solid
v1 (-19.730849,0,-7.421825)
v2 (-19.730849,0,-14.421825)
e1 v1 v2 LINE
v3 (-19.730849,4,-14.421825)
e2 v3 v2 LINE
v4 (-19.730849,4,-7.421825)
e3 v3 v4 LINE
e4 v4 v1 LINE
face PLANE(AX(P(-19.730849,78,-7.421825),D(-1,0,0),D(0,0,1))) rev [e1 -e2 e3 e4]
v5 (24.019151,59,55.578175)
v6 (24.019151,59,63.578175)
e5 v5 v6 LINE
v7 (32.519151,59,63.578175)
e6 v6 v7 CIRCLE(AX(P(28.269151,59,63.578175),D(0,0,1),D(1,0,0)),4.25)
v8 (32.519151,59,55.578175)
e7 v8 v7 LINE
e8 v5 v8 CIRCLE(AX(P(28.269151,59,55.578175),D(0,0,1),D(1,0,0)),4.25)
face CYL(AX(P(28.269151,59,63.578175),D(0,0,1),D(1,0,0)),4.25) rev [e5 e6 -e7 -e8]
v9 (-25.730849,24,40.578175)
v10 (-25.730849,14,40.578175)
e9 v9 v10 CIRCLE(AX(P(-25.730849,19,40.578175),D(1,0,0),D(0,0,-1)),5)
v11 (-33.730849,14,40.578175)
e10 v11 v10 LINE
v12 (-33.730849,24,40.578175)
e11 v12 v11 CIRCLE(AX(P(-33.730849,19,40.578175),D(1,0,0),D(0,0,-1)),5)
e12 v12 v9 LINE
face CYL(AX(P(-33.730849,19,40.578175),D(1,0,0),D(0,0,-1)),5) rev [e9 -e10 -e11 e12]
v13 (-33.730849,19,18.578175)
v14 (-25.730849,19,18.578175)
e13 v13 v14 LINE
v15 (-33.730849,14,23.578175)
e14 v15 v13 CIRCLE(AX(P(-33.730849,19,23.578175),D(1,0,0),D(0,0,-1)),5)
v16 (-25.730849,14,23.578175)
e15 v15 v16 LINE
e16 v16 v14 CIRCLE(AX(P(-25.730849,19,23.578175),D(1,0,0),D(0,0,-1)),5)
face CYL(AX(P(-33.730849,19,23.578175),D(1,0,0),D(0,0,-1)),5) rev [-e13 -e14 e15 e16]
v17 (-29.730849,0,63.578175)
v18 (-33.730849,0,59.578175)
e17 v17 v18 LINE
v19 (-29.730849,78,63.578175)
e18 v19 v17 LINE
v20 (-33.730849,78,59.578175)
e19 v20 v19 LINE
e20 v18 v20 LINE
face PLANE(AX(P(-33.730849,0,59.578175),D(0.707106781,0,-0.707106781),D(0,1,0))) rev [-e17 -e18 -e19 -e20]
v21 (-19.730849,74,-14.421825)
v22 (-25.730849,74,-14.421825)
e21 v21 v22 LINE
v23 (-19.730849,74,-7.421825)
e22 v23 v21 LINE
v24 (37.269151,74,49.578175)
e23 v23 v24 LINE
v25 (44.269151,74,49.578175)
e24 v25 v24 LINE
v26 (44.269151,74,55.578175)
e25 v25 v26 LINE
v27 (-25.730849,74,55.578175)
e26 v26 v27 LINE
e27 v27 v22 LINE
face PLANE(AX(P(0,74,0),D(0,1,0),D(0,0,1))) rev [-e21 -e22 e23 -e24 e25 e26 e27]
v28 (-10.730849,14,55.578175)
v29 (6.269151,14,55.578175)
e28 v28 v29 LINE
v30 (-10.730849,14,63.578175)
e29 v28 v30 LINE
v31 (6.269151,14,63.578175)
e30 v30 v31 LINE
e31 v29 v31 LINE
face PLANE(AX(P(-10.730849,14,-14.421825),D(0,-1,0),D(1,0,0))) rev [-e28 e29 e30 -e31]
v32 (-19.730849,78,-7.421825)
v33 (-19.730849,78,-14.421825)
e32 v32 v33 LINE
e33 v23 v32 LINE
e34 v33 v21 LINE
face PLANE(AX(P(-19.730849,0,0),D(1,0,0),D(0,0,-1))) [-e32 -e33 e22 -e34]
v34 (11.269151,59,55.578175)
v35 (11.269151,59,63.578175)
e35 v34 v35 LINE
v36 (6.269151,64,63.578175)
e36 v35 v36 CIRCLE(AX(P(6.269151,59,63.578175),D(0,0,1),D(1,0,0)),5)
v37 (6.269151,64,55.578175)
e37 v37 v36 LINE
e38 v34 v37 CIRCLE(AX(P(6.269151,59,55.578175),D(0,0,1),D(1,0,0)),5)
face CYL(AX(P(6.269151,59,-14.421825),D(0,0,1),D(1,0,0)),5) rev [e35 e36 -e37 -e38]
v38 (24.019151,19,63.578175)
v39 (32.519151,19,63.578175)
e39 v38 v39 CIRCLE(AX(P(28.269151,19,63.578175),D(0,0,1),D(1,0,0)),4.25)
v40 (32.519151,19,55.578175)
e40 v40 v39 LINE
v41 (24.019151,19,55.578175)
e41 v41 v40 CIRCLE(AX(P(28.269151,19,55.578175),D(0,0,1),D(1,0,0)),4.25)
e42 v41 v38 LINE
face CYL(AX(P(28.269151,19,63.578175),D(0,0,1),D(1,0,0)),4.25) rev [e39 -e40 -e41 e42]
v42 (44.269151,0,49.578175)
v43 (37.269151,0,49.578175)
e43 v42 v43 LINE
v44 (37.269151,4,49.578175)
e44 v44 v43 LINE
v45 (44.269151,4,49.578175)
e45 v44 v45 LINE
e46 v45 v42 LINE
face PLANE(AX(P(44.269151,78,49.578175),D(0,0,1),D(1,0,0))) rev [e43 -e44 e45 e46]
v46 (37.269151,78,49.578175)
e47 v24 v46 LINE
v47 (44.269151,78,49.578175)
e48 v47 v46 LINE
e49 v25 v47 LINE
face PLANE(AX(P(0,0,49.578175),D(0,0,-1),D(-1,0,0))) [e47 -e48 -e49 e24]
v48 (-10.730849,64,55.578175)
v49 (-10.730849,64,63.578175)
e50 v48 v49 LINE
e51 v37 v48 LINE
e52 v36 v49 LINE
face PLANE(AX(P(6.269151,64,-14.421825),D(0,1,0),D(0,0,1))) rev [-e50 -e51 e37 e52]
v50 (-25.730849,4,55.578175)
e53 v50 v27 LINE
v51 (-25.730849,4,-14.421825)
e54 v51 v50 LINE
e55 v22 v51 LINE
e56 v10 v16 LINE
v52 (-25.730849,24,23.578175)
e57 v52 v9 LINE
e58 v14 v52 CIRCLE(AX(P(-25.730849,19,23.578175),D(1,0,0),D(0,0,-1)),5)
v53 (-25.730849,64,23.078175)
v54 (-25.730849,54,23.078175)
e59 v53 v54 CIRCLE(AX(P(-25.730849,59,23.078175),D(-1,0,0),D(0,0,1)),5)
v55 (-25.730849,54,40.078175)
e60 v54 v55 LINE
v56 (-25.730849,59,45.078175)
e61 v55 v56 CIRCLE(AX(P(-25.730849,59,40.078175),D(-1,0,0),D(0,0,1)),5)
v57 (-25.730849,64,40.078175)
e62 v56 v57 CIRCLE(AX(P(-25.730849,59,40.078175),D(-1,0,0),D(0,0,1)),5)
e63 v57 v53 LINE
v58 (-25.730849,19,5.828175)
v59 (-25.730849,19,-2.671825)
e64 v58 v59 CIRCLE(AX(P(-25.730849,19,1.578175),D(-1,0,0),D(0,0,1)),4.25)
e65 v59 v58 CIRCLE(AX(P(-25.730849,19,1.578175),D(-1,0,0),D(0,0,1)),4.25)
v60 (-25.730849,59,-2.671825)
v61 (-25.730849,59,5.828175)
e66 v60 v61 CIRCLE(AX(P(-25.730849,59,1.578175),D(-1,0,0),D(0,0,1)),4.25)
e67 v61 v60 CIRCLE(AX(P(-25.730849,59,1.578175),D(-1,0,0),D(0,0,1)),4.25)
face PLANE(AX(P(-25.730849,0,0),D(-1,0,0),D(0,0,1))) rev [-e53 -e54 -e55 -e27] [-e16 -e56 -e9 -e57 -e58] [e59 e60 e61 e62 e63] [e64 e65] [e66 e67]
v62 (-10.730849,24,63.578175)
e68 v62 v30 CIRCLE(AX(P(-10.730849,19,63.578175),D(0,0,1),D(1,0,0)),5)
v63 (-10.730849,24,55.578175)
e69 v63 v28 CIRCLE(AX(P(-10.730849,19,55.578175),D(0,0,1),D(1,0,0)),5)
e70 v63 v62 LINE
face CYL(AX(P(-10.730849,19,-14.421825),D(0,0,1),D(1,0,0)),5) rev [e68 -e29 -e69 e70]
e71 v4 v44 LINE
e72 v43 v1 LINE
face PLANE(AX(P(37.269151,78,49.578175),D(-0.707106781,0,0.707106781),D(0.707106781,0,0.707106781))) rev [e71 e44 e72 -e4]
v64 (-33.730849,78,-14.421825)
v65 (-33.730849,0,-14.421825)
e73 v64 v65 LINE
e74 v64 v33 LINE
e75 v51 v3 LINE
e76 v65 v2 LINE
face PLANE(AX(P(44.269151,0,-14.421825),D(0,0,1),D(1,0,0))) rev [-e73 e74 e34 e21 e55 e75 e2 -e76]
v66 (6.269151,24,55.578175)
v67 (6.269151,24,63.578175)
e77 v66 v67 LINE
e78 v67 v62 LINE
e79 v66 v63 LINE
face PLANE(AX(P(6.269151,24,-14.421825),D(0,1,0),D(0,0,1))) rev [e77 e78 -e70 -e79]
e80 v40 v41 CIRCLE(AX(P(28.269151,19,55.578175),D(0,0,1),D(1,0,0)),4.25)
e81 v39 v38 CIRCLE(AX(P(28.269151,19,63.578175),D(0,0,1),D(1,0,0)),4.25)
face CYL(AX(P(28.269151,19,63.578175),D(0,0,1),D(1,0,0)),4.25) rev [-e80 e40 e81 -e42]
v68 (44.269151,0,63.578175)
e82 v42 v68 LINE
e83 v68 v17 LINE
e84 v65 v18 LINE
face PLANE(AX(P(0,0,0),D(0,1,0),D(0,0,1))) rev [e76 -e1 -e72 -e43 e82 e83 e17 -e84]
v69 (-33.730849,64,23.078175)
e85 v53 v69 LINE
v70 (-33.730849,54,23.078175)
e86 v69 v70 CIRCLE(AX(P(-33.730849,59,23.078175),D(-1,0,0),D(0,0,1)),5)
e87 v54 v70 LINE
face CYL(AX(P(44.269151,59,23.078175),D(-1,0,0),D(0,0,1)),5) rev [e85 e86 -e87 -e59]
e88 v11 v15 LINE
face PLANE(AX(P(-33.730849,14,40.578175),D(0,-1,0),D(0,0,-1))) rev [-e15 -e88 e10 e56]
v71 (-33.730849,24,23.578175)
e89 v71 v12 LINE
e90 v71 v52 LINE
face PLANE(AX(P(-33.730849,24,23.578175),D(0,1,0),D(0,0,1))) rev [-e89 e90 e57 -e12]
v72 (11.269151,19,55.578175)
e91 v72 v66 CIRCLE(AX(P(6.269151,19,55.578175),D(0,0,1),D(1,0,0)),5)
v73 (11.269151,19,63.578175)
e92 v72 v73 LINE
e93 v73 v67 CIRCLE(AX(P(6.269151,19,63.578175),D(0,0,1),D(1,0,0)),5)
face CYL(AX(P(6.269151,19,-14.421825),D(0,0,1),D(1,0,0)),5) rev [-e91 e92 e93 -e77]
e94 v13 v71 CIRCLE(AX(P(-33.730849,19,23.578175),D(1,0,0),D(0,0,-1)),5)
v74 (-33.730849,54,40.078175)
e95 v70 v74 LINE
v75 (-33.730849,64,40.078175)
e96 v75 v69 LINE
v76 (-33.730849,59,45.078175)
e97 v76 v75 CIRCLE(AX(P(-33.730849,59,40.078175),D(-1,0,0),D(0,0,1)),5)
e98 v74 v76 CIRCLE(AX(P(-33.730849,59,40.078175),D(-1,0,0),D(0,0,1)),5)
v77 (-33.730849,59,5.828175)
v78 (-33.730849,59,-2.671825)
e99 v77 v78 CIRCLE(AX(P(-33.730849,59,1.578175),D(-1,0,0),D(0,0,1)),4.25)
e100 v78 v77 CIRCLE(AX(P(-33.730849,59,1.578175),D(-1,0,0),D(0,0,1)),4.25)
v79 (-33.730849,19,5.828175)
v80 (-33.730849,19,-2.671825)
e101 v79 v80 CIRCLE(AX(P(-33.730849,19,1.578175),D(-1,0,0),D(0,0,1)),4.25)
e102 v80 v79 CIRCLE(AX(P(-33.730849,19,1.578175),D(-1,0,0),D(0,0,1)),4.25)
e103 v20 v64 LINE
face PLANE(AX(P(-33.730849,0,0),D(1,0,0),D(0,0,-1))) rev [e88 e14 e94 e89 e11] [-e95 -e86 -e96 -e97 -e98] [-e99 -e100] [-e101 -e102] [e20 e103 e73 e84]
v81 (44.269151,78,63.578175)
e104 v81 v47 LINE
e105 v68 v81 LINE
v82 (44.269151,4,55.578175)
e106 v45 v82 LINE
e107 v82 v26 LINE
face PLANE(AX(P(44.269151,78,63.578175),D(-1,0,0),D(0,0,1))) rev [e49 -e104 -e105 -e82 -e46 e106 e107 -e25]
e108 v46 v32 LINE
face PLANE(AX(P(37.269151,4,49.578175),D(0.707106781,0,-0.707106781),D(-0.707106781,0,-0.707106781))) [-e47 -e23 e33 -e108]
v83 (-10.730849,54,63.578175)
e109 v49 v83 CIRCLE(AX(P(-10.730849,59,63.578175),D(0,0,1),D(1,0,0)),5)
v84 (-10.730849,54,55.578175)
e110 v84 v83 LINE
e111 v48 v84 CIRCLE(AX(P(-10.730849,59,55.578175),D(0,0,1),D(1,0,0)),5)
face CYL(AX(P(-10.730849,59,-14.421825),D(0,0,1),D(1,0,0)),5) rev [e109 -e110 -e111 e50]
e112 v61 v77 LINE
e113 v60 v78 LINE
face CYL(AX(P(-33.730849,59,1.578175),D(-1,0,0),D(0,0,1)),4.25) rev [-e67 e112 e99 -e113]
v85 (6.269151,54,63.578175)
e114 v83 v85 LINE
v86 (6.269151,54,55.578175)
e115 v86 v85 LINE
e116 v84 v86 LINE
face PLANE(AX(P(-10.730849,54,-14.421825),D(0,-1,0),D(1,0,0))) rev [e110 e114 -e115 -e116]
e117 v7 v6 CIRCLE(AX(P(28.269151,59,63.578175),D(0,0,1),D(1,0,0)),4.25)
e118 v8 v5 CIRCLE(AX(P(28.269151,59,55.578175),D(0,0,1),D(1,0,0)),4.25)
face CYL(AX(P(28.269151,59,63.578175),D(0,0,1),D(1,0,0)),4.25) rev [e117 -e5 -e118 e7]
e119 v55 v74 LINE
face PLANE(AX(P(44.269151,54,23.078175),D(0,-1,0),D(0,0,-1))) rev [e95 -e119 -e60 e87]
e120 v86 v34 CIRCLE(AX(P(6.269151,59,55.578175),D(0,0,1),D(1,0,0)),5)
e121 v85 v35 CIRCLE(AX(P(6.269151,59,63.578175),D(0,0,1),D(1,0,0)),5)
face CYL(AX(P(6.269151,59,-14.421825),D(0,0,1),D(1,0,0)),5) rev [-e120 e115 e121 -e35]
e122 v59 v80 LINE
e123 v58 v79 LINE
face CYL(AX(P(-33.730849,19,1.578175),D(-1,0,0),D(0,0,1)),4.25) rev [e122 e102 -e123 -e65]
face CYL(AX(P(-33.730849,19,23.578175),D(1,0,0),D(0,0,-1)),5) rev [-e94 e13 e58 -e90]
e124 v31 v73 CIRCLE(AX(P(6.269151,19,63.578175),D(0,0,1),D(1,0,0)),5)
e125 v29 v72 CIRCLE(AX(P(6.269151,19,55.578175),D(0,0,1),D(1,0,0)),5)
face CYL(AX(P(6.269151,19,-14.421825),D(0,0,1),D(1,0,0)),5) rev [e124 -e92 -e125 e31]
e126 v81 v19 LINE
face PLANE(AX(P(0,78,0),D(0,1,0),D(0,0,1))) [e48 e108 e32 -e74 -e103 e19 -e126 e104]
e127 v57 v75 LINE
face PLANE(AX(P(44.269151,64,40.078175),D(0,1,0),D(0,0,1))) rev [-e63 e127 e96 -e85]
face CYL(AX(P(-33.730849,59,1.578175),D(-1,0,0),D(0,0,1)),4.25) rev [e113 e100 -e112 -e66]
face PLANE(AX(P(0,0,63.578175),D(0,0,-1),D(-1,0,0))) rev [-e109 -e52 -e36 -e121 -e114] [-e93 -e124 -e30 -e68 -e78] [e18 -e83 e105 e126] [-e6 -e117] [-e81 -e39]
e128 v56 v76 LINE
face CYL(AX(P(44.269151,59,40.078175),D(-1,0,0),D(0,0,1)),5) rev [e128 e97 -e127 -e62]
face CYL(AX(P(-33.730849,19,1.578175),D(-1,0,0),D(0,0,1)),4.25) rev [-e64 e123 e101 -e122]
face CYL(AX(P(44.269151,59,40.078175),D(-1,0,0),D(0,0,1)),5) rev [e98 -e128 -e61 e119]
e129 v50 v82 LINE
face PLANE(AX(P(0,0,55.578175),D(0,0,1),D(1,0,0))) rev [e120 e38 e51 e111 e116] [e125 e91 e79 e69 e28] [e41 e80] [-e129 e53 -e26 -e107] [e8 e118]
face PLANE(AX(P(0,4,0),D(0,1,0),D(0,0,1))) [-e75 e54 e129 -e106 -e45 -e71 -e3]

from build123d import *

# Parameters (mm, degrees)
BOSS_EXTRUDE1_DEPTH            = 74
SKETCH2_W                      = 64
SKETCH2_H                      = 74
BOSS_EXTRUDE2_DEPTH            = 14
SKETCH3_W                      = 64
SKETCH3_H                      = 78
BOSS_EXTRUDE3_DEPTH            = 4
CUT_EXTRUDE1_DEPTH             = 70
SKETCH5_W                      = 78
SKETCH5_H                      = 78
BOSS_EXTRUDE4_DEPTH            = 14
CUT_EXTRUDE2_REACH             = 115.771
SKETCH7_W                      = 64
SKETCH7_H                      = 70
CUT_EXTRUDE3_REACH             = 124.581
SKETCH9_W                      = 70
SKETCH9_H                      = 70
CUT_EXTRUDE4_DEPTH             = 110.936081615
CUT_EXTRUDE5_DEPTH             = 123.581337469
CUT_EXTRUDE6_DEPTH             = 119.860244595
CUT_EXTRUDE7_DEPTH             = 119.860244595
CUT_EXTRUDE8_DEPTH             = 128.31922202
F_8_5_8_5_DIAMETER_HOLE1_D     = 8.5
F_8_5_8_5_DIAMETER_HOLE1_DEPTH = 78
F_8_5_8_5_DIAMETER_HOLE2_D     = 8.5
F_8_5_8_5_DIAMETER_HOLE2_DEPTH = 78
CHAMFER1_SIZE                  = 4


with BuildPart() as part:
    # Sketch1 → Boss-Extrude1 (new body)
    with BuildSketch(Plane(origin=(0, 78, 0), x_dir=(1, 0, 0), z_dir=(0, 1, 0))):
        Polygon((-19.730848831, -49.578174681), (37.269151169, -49.578174681), (-19.730848831, 7.421825319), align=None)
    extrude(amount=-BOSS_EXTRUDE1_DEPTH)

    # Sketch2 → Boss-Extrude2 (add)
    with BuildSketch(Plane.XY.offset(49.578174681)):
        with Locations((12.269151169, 41)):
            Rectangle(SKETCH2_W, SKETCH2_H)
    extrude(amount=BOSS_EXTRUDE2_DEPTH)

    # Sketch3 → Boss-Extrude3 (add)
    with BuildSketch(Plane.XZ.offset(-4)):
        with Locations((12.269151169, 24.578174681)):
            Rectangle(SKETCH3_W, SKETCH3_H)
    extrude(amount=BOSS_EXTRUDE3_DEPTH)

    # Sketch4 → Cut-Extrude1 (cut)
    with BuildSketch(Plane.XZ.offset(-4)):
        Polygon((-19.730848831, -7.421825319), (37.269151169, 49.578174681), (-19.730848831, 49.578174681), align=None)
    extrude(amount=-CUT_EXTRUDE1_DEPTH, mode=Mode.SUBTRACT)

    # Sketch5 → Boss-Extrude4 (add)
    with BuildSketch(Plane.ZY.offset(19.730848831)):
        with Locations((24.578174681, 39)):
            Rectangle(SKETCH5_W, SKETCH5_H)
    extrude(amount=BOSS_EXTRUDE4_DEPTH)

    # Sketch7 → Cut-Extrude2 (cut, up to next)
    with BuildSketch(Plane.XY.offset(55.578174681), mode=Mode.PRIVATE) as cut_extrude2_sk1:
        with Locations((12.269151169, 39)):
            Rectangle(SKETCH7_W, SKETCH7_H)
    cut_extrude2_tool1 = extrude(cut_extrude2_sk1.sketch, amount=-CUT_EXTRUDE2_REACH, mode=Mode.PRIVATE) & part.part
    add(cut_extrude2_tool1.solids().sort_by_distance((12.269151, 39, 55.578175))[0], mode=Mode.SUBTRACT)

    # Sketch9 → Cut-Extrude3 (cut, up to next)
    with BuildSketch(Plane(origin=(-25.730848831, 0, 0), x_dir=(0, -1, 0), z_dir=(-1, 0, 0)), mode=Mode.PRIVATE) as cut_extrude3_sk1:
        with Locations((-39, 20.578174681)):
            Rectangle(SKETCH9_W, SKETCH9_H)
    cut_extrude3_tool1 = extrude(cut_extrude3_sk1.sketch, amount=-CUT_EXTRUDE3_REACH, mode=Mode.PRIVATE) & part.part
    add(cut_extrude3_tool1.solids().sort_by_distance((-25.730849, 39, 20.578175))[0], mode=Mode.SUBTRACT)

    # Sketch10 → Cut-Extrude4 (cut, through all)
    with BuildSketch(Plane.XZ):
        Polygon((44.269151169, 49.578174681), (37.269151169, 49.578174681), (-19.730848831, -7.421825319), (-19.730848831, -14.421825319), (44.269151169, -14.421825319), align=None)
    extrude(amount=-CUT_EXTRUDE4_DEPTH, mode=Mode.SUBTRACT)

    # Sketch11 → Cut-Extrude5 (cut, through all)
    with BuildSketch(Plane(origin=(-25.730848831, 0, 0), x_dir=(0, 0, -1), z_dir=(1, 0, 0))):
        with BuildLine():
            Line((-23.578174681, 24), (-40.578174681, 24))
            ThreePointArc((-40.578174681, 24), (-45.578174681, 19), (-40.578174681, 14))
            Line((-40.578174681, 14), (-23.578174681, 14))
            ThreePointArc((-23.578174681, 14), (-18.578174681, 19), (-23.578174681, 24))
        make_face()
    extrude(amount=-CUT_EXTRUDE5_DEPTH, mode=Mode.SUBTRACT)

    # Sketch12 → Cut-Extrude6 (cut, through all)
    with BuildSketch(Plane.XY.offset(63.578174681)):
        with BuildLine():
            Line((6.269151169, 64), (-10.730848831, 64))
            ThreePointArc((-10.730848831, 64), (-15.730848831, 59), (-10.730848831, 54))
            Line((-10.730848831, 54), (6.269151169, 54))
            ThreePointArc((6.269151169, 54), (11.269151169, 59), (6.269151169, 64))
        make_face()
    extrude(amount=-CUT_EXTRUDE6_DEPTH, mode=Mode.SUBTRACT)

    # Sketch13 → Cut-Extrude7 (cut, through all)
    with BuildSketch(Plane.XY.offset(63.578174681)):
        with BuildLine():
            Line((6.269151169, 24), (-10.730848831, 24))
            ThreePointArc((-10.730848831, 24), (-15.730848831, 19), (-10.730848831, 14))
            Line((-10.730848831, 14), (6.269151169, 14))
            ThreePointArc((6.269151169, 14), (11.269151169, 19), (6.269151169, 24))
        make_face()
    extrude(amount=-CUT_EXTRUDE7_DEPTH, mode=Mode.SUBTRACT)

    # Sketch14 → Cut-Extrude8 (cut, through all)
    with BuildSketch(Plane.ZY.offset(33.730848831)):
        with BuildLine():
            Line((23.078174681, 54), (40.078174681, 54))
            ThreePointArc((40.078174681, 54), (45.078174681, 59), (40.078174681, 64))
            Line((40.078174681, 64), (23.078174681, 64))
            ThreePointArc((23.078174681, 64), (18.078174681, 59), (23.078174681, 54))
        make_face()
    extrude(amount=-CUT_EXTRUDE8_DEPTH, mode=Mode.SUBTRACT)

    # Ø8.5 (8.5) Diameter Hole1
    with Locations(Plane.ZY.offset(33.730848831)):
        with Locations((1.578174681, 59), (1.578174681, 19)):
            Hole(F_8_5_8_5_DIAMETER_HOLE1_D / 2, depth=F_8_5_8_5_DIAMETER_HOLE1_DEPTH)

    # Ø8.5 (8.5) Diameter Hole2
    with Locations(Plane.XY.offset(63.578174681)):
        with Locations((28.269151169, 19), (28.269151169, 59)):
            Hole(F_8_5_8_5_DIAMETER_HOLE2_D / 2, depth=F_8_5_8_5_DIAMETER_HOLE2_DEPTH)

    # Chamfer1
    chamfer1_edges = [part.edges().sort_by_distance(p)[0] for p in [
        (-33.730848831, 39, 63.578174681),
    ]]
    chamfer(chamfer1_edges, length=CHAMFER1_SIZE)


solid = part.part
